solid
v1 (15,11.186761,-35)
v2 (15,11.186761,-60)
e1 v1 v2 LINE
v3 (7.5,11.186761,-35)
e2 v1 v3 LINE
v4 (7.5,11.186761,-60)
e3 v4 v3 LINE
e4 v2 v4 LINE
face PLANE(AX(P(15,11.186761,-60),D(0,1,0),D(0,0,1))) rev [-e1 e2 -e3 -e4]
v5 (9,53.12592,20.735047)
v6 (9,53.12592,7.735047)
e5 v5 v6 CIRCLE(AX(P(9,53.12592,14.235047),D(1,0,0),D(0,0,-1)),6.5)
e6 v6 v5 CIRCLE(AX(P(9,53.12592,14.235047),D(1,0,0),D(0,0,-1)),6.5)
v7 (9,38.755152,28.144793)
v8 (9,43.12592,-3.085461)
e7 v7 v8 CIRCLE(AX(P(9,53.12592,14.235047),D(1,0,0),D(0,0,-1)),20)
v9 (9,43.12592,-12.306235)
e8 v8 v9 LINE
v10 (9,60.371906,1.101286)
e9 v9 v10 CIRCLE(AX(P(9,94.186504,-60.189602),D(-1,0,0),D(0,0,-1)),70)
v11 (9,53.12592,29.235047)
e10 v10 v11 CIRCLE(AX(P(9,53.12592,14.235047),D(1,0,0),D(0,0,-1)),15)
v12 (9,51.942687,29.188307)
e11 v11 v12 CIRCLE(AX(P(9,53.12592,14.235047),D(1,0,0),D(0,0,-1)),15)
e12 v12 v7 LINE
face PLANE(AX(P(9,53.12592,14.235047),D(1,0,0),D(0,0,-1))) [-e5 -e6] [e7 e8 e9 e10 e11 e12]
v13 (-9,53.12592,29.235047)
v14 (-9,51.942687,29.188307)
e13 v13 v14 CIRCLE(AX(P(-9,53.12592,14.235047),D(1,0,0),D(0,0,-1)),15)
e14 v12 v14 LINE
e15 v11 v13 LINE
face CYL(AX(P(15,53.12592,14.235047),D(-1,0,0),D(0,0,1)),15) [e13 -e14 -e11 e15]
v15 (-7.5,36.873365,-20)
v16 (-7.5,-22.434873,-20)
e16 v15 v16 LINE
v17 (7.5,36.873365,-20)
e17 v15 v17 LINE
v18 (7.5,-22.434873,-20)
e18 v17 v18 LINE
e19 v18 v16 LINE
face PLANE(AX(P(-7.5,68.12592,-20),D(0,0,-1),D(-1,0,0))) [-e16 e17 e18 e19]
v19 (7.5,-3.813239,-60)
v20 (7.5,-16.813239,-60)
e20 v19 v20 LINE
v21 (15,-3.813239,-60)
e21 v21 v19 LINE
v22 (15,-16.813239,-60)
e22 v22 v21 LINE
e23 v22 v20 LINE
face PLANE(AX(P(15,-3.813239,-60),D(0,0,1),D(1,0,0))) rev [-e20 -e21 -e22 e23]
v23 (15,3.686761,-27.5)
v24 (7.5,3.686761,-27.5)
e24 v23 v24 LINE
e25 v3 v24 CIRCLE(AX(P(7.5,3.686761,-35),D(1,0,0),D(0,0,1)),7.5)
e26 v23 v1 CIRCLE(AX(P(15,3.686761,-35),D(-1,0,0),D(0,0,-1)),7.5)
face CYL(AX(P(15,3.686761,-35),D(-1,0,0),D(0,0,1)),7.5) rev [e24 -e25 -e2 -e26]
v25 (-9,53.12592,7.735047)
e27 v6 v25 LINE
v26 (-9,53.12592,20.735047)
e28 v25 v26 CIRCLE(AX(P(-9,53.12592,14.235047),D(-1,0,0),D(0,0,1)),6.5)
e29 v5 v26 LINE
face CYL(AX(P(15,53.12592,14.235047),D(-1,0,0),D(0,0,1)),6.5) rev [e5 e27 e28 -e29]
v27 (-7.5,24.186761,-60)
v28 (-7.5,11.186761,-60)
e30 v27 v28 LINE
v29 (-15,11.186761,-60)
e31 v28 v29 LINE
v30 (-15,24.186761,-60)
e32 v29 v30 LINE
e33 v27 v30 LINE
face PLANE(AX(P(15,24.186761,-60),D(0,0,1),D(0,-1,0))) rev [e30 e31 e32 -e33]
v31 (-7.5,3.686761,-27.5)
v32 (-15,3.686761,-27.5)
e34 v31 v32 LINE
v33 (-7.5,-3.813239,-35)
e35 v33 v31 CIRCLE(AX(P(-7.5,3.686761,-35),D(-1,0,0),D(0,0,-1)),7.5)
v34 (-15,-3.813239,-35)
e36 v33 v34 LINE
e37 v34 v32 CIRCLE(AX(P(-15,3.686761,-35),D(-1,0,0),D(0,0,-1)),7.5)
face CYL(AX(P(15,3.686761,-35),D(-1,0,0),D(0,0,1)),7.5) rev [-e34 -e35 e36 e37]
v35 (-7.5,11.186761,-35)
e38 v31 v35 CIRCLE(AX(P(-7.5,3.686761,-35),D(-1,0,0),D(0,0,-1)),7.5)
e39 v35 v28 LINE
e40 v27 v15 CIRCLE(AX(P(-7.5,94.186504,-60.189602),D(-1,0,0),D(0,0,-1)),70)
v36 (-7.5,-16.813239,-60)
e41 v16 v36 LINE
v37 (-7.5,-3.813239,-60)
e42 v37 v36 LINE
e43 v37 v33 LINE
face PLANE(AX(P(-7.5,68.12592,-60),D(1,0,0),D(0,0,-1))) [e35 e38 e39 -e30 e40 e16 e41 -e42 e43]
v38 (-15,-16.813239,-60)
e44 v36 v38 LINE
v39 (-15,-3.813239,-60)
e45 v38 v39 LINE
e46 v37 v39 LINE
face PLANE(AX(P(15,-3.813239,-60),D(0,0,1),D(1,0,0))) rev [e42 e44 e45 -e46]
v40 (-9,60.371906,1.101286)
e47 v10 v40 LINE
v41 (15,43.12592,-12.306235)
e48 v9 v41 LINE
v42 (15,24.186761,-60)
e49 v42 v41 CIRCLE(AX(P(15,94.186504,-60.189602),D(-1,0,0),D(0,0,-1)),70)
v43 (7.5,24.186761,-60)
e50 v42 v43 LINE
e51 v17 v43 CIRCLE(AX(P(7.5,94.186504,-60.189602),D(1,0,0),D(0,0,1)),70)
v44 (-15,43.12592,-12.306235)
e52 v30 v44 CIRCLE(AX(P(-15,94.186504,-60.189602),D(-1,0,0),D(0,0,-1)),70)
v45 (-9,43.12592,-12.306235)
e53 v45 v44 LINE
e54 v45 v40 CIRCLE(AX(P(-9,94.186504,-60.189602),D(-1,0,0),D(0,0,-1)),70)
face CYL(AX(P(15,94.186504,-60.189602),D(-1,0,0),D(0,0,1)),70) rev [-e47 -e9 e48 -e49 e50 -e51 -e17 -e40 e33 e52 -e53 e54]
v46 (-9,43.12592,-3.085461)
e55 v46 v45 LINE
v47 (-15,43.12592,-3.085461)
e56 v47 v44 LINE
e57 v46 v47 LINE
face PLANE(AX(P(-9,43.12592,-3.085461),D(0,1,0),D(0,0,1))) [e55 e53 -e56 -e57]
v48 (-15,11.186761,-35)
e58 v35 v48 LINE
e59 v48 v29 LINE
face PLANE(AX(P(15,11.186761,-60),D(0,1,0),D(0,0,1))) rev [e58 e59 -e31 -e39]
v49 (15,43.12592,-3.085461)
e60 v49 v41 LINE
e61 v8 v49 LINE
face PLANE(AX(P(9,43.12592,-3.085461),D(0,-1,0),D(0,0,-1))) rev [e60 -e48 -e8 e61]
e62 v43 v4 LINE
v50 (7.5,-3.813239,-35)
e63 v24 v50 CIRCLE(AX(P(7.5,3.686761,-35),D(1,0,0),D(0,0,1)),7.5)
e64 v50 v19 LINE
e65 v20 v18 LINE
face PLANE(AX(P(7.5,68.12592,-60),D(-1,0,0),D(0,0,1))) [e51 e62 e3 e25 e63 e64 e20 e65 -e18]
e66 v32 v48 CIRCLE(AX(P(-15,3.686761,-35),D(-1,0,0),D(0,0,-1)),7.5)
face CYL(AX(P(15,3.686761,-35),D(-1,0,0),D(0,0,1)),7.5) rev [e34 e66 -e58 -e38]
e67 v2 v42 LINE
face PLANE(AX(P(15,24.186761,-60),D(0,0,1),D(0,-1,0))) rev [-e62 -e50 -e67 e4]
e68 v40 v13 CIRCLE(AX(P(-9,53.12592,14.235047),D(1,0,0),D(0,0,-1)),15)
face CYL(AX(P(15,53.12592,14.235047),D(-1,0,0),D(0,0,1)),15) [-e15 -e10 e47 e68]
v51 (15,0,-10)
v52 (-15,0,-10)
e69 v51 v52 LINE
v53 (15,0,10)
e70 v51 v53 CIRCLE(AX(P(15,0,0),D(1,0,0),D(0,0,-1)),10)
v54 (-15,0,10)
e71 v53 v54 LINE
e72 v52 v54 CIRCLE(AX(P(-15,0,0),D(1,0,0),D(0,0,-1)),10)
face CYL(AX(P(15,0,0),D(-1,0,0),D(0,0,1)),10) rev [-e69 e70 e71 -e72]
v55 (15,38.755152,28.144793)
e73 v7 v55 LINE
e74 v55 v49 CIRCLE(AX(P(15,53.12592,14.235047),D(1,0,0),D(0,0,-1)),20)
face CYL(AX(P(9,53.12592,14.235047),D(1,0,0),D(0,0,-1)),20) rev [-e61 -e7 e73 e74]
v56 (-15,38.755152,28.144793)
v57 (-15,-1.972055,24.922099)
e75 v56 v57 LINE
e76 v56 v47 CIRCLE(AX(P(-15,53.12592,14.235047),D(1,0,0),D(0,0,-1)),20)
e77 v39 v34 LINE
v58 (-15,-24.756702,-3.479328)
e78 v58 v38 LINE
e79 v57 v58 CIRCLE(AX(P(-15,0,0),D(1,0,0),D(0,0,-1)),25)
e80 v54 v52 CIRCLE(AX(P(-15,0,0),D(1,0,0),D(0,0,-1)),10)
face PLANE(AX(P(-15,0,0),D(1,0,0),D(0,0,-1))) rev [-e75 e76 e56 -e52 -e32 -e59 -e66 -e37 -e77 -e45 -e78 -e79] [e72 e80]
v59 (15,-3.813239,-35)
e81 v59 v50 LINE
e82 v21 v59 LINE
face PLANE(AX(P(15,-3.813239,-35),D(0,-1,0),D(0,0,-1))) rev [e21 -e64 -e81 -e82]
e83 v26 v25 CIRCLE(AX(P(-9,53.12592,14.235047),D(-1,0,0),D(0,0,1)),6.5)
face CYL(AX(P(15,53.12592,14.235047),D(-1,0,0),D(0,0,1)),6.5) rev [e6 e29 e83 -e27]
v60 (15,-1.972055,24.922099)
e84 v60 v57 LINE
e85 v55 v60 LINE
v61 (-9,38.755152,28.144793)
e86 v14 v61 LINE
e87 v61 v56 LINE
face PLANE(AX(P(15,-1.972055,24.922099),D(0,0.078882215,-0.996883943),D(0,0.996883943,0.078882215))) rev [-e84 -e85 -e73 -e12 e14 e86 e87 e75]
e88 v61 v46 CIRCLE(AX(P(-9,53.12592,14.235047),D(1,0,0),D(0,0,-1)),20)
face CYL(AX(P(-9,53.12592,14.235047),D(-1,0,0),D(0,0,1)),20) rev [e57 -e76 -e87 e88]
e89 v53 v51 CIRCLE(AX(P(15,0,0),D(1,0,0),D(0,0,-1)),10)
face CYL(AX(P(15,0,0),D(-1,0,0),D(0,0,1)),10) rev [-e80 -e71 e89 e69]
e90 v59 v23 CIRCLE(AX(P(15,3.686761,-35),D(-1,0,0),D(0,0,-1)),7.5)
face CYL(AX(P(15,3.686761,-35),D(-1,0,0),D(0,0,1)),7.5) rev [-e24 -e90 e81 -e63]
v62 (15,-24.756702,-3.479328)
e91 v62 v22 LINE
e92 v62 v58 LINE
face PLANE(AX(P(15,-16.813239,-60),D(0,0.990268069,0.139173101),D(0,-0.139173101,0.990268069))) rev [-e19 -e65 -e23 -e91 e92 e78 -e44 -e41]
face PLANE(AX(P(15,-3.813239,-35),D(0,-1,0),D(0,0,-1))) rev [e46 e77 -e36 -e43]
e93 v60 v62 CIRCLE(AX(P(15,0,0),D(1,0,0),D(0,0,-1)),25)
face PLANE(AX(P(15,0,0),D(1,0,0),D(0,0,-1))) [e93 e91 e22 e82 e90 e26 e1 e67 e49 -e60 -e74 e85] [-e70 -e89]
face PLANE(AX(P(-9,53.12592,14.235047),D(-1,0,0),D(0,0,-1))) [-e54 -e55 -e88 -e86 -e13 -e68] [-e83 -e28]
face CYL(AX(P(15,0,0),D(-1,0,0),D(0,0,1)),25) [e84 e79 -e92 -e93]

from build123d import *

# Parameters (mm, degrees)
BRACKET_PROFILE_SKETCH_R       = 10
BRACKET_PROFILE_SKETCH_R_2     = 6.5
BRACKET_BODY_30_THICK_DEPTH    = 15
SIDE_STEP_CUT_20X10X6_DEPTH    = 6
FORKED_SLOT_15_WIDE_DEPTH      = 93.011635333
FORKED_SLOT_15_WIDE_DEPTH_BACK = 93.011635333
FORK_SLOT_SKETCH_W             = 15
FORK_SLOT_SKETCH_H             = 40


with BuildPart() as part:
    # Bracket Profile Sketch → Bracket Body 30 Thick (new, symmetric)
    with BuildSketch(Plane(origin=(0, 0, 0), x_dir=(0, 0, -1), z_dir=(1, 0, 0))):
        with BuildLine():
            Line((-24.92209858, -1.972055368), (-29.188306629, 51.942687225))
            ThreePointArc((-29.188306629, 51.942687225), (-18.546726282, 67.492876488), (-1.101285774, 60.371905777))
            ThreePointArc((-1.101285774, 60.371905777), (24.520233718, 33.956144929), (60, 24.186760769))
            Line((60, 24.186760769), (60, 11.186760769))
            Line((60, 11.186760769), (35, 11.186760769))
            ThreePointArc((35, 11.186760769), (27.5, 3.686760769), (35, -3.813239231))
            Line((35, -3.813239231), (60, -3.813239231))
            Line((60, -3.813239231), (60, -16.813239231))
            Line((60, -16.813239231), (3.479327524, -24.756701719))
            ThreePointArc((3.479327524, -24.756701719), (-15.643948829, -19.500432432), (-24.92209858, -1.972055368))
        make_face()
        Circle(BRACKET_PROFILE_SKETCH_R, mode=Mode.SUBTRACT)
        with Locations((-14.235047481, 53.125920446)):
            Circle(BRACKET_PROFILE_SKETCH_R_2, mode=Mode.SUBTRACT)
    extrude(amount=BRACKET_BODY_30_THICK_DEPTH, both=True)

    # Side Step Sketch → Side Step Cut 20x10x6 (cut)
    with BuildSketch(Plane(origin=(15, 0, 0), x_dir=(0, 0, -1), z_dir=(1, 0, 0))):
        with BuildLine():
            Line((3.085460595, 43.125920446), (12.306235476, 43.125920446))
            ThreePointArc((12.306235476, 43.125920446), (4.925595155, 51.222687515), (-1.101285774, 60.371905777))
            ThreePointArc((-1.101285774, 60.371905777), (-18.546726282, 67.492876488), (-29.188306629, 51.942687225))
            Line((-29.188306629, 51.942687225), (-28.144793013, 38.755152227))
            ThreePointArc((-28.144793013, 38.755152227), (-11.463003291, 33.318957756), (3.085460595, 43.125920446))
        make_face()
    side_step_cut_20x10x6 = extrude(amount=-SIDE_STEP_CUT_20X10X6_DEPTH, mode=Mode.SUBTRACT)

    # Side Step Cut Mirror: Side Step Cut 20x10x6 across plane
    add(side_step_cut_20x10x6.mirror(Plane(origin=(0, 0, 0), x_dir=(0, 0, 1), z_dir=(1, 0, 0))), mode=Mode.SUBTRACT)

    # Fork Slot Sketch → Forked Slot 15 Wide (cut, two sides: drawn at the far end of the back side and taken through both)
    with BuildSketch(Plane(origin=(0, 0, 0), x_dir=(1, 0, 0), z_dir=(0, 1, 0)).offset(-FORKED_SLOT_15_WIDE_DEPTH_BACK)):
        with Locations((0, 40)):
            Rectangle(FORK_SLOT_SKETCH_W, FORK_SLOT_SKETCH_H)
    extrude(amount=FORKED_SLOT_15_WIDE_DEPTH + FORKED_SLOT_15_WIDE_DEPTH_BACK, mode=Mode.SUBTRACT)


solid = part.part
